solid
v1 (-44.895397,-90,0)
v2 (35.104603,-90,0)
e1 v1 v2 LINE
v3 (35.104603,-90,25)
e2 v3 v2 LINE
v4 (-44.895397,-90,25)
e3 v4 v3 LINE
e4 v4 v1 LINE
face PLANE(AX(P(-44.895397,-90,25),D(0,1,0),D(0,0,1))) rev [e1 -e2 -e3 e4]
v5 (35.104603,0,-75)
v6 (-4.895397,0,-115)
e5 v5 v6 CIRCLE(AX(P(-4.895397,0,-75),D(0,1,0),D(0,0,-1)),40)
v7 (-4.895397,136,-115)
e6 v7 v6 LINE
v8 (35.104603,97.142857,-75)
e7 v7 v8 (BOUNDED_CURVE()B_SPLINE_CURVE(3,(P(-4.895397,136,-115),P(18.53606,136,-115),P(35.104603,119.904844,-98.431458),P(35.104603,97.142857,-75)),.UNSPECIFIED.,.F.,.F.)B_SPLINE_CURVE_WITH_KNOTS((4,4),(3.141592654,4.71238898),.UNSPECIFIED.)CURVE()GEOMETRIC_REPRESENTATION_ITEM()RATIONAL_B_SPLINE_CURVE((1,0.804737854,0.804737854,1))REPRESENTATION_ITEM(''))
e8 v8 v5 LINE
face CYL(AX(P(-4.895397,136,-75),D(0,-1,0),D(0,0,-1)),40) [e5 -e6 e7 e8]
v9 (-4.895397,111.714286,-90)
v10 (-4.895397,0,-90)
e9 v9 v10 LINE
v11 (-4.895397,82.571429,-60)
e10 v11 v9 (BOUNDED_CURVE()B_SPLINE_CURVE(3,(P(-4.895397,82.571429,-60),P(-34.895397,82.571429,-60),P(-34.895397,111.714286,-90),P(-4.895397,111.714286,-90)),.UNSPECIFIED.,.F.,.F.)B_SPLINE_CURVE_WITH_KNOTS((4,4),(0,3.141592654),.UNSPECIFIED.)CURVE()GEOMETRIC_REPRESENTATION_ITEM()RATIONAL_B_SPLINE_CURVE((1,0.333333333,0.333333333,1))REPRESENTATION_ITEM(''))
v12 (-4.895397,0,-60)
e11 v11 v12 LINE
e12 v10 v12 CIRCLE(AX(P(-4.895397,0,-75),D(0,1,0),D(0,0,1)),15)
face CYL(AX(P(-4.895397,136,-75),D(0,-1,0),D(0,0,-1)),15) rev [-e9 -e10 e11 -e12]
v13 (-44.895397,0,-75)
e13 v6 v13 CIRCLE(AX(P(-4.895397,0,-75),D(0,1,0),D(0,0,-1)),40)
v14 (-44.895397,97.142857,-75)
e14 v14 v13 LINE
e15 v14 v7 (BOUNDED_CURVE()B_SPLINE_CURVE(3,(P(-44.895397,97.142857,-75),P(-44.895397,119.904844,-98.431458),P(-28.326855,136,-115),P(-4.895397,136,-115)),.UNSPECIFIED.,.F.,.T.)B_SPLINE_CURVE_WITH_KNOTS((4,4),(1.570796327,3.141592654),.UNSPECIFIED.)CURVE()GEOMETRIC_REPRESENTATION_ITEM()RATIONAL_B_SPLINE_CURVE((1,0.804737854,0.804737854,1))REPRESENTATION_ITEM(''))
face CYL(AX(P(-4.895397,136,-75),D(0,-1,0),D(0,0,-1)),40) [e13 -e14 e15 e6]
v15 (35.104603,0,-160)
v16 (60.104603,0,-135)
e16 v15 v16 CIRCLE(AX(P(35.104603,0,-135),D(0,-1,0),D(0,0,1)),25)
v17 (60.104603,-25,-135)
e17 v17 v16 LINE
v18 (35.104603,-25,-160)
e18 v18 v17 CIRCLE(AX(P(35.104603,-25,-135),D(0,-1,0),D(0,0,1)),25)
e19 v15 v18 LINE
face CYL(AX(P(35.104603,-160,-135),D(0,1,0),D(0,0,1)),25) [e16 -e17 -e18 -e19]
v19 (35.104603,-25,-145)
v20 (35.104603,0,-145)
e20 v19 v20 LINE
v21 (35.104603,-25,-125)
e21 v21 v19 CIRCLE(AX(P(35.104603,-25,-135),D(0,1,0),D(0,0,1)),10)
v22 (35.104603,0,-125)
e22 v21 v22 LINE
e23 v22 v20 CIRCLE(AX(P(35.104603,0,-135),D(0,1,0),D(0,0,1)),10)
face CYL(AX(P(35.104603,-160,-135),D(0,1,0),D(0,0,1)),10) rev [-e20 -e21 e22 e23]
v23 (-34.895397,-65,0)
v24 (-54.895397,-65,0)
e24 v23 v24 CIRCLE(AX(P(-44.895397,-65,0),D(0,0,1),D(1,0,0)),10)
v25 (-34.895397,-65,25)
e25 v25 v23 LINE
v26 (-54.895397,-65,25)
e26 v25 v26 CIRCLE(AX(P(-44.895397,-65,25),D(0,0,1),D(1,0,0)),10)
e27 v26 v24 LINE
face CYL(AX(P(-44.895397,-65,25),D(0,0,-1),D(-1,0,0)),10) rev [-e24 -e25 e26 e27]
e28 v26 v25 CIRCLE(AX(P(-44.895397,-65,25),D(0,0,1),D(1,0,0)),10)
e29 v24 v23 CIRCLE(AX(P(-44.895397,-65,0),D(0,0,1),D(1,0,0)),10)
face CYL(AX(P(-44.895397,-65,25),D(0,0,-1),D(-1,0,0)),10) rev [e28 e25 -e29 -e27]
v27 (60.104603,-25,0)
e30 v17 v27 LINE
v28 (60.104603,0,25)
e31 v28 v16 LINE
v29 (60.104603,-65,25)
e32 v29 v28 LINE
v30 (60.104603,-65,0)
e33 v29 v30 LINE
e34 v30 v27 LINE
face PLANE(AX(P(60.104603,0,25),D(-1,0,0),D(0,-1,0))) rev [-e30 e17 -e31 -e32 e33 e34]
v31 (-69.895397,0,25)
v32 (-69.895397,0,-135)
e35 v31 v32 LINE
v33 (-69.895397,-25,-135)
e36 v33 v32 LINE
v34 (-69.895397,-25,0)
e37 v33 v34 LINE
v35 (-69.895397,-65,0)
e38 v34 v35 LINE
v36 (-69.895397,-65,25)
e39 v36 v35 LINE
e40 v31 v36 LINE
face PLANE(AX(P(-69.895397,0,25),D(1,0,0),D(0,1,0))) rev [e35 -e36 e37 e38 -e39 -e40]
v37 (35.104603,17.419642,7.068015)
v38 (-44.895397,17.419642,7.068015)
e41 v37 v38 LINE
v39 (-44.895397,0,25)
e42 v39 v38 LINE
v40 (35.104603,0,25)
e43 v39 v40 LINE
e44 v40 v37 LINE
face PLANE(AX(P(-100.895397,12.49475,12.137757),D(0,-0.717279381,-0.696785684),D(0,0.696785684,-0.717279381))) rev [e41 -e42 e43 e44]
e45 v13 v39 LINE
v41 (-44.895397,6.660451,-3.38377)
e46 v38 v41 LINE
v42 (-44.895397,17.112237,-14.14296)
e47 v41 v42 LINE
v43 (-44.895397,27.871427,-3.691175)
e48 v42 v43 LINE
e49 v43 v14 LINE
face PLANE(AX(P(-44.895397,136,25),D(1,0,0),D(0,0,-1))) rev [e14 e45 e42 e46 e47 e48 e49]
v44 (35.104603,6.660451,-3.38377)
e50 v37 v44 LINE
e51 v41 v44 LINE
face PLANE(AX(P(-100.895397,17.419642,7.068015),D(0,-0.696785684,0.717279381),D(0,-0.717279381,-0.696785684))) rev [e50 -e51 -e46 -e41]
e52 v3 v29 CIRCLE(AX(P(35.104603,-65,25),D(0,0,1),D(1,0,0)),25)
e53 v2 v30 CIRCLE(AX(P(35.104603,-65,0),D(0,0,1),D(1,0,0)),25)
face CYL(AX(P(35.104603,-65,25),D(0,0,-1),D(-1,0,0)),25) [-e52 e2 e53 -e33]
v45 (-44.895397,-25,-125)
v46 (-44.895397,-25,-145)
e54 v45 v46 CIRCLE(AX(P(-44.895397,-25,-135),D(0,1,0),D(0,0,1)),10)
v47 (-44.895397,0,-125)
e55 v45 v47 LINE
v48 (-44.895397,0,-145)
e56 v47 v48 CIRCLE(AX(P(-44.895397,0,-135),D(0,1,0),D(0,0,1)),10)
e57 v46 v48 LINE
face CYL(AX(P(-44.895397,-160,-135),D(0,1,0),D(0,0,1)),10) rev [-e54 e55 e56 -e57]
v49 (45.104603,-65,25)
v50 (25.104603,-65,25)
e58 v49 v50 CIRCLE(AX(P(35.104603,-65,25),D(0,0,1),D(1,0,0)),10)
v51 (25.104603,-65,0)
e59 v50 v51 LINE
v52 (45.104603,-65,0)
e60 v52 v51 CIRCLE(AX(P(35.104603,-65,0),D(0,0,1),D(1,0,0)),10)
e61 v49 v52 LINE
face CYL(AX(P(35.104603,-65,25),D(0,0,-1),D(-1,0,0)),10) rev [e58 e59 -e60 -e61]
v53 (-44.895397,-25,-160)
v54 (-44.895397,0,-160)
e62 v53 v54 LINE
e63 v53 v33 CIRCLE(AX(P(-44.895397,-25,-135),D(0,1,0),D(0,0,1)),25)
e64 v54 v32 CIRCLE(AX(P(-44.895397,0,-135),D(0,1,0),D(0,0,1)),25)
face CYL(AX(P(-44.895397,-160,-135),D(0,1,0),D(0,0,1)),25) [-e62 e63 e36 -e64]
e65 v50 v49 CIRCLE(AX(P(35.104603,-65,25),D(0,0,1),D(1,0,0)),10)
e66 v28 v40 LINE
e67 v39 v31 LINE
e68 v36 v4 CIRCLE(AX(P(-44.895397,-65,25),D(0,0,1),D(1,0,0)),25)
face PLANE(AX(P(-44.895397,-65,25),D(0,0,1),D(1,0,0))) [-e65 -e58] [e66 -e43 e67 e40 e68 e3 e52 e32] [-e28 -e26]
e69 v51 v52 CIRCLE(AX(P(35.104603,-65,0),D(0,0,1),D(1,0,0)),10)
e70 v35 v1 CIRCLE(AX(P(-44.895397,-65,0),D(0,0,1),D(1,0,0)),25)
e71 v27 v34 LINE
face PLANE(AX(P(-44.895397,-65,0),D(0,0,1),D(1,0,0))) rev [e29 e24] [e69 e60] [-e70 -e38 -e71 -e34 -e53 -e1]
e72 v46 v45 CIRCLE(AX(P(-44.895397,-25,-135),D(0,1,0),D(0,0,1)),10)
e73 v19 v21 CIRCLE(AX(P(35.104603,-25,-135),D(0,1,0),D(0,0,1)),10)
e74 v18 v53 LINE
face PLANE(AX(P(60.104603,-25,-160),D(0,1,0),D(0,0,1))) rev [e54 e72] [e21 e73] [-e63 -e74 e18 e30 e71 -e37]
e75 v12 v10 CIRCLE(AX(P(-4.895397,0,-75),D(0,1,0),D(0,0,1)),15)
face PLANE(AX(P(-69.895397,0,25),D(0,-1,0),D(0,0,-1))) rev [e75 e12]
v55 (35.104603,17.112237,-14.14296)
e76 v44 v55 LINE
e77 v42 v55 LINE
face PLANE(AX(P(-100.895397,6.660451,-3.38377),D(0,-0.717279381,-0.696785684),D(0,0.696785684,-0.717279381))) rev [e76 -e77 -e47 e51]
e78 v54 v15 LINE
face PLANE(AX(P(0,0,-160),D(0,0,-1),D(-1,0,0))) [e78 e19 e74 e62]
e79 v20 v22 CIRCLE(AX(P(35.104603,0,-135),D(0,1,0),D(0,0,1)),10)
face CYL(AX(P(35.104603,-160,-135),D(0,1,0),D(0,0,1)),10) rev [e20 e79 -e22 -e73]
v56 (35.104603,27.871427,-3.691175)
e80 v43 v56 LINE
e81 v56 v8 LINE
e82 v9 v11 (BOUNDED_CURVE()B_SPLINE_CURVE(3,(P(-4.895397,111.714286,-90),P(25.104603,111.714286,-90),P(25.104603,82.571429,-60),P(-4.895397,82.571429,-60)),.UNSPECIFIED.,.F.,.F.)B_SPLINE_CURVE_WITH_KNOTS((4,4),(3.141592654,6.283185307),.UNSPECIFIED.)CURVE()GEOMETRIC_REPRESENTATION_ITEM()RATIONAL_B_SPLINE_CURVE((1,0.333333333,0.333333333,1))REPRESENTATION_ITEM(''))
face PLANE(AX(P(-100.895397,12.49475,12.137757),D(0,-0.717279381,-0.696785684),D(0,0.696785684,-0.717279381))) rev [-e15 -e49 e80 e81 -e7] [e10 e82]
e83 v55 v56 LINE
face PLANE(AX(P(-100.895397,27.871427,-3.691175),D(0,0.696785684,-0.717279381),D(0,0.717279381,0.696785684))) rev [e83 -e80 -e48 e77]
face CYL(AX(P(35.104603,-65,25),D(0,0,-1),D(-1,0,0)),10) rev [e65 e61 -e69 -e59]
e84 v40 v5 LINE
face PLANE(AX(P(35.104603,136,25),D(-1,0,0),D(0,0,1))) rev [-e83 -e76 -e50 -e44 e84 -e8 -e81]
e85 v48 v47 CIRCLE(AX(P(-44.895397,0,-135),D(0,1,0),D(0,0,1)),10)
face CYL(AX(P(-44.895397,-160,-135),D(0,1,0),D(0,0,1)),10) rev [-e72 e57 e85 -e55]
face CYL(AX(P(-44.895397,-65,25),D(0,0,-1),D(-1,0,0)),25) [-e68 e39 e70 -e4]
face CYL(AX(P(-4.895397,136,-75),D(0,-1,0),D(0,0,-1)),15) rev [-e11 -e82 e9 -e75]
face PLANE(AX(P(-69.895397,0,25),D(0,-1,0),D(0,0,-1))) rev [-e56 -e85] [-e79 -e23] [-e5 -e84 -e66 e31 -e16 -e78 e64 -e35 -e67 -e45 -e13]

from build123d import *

# Parameters (mm, degrees)
BASE_PLATE_SKETCH_R      = 10
BASE_PLATE_DEPTH         = 25
FLANGE_SKETCH_W          = 130
FLANGE_SKETCH_H          = 25
FLANGE_DEPTH             = 160
FLANGE_PROFILE_CUT_DEPTH = 160
HOLES_SKETCH_R           = 10
HOLES_CUT_DEPTH          = 160
LUG_SKETCH_R             = 15
LUG_DEPTH                = 136
LUG_45DEG_TRIM_DEPTH     = 136
LUG_NOTCH_DEPTH          = 136


with BuildPart() as part:
    # Base Plate Sketch → Base Plate (new body)
    with BuildSketch(Plane.XY):
        with BuildLine():
            Line((-69.89539749, 0), (60.10460251, 0))
            Line((60.10460251, 0), (60.10460251, -65))
            ThreePointArc((60.10460251, -65), (52.78227204, -82.67766953), (35.10460251, -90))
            Line((35.10460251, -90), (-44.89539749, -90))
            ThreePointArc((-44.89539749, -90), (-62.573067019, -82.67766953), (-69.89539749, -65))
            Line((-69.89539749, -65), (-69.89539749, 0))
        make_face()
        with Locations((-44.89539749, -65)):
            Circle(BASE_PLATE_SKETCH_R, mode=Mode.SUBTRACT)
        with Locations((35.10460251, -65)):
            Circle(BASE_PLATE_SKETCH_R, mode=Mode.SUBTRACT)
    extrude(amount=BASE_PLATE_DEPTH)

    # Flange Sketch → Flange (add)
    with BuildSketch(Plane(origin=(0, 0, 0), x_dir=(-1, 0, 0), z_dir=(0, 0, -1))):
        with Locations((4.89539749, -12.5)):
            Rectangle(FLANGE_SKETCH_W, FLANGE_SKETCH_H)
    extrude(amount=FLANGE_DEPTH)

    # Flange Profile Cut Sketch → Flange Profile Cut (cut)
    with BuildSketch(Plane(origin=(0, 0, 0), x_dir=(1, 0, 0), z_dir=(0, 1, 0))):
        with BuildLine():
            Line((60.10460251, 160), (35.10460251, 160))
            ThreePointArc((35.10460251, 160), (52.78227204, 152.67766953), (60.10460251, 135))
            Line((60.10460251, 135), (60.10460251, 160))
        make_face()
        with BuildLine():
            ThreePointArc((-69.89539749, 135), (-62.573067019, 152.67766953), (-44.89539749, 160))
            Line((-44.89539749, 160), (-69.89539749, 160))
            Line((-69.89539749, 160), (-69.89539749, 135))
        make_face()
    extrude(amount=-FLANGE_PROFILE_CUT_DEPTH, mode=Mode.SUBTRACT)

    # Holes Sketch → Holes Cut (cut)
    with BuildSketch(Plane(origin=(0, 0, 0), x_dir=(1, 0, 0), z_dir=(0, 1, 0))):
        with Locations(Location((-44.89539749, 135, 0), (0, 0, 270))):
            Circle(HOLES_SKETCH_R)
        with Locations(Location((35.10460251, 135, 0), (0, 0, 270))):
            Circle(HOLES_SKETCH_R)
    extrude(amount=-HOLES_CUT_DEPTH, mode=Mode.SUBTRACT)

    # Lug Sketch → Lug (add)
    with BuildSketch(Plane(origin=(0, 0, 0), x_dir=(1, 0, 0), z_dir=(0, 1, 0))):
        with BuildLine():
            Line((-44.89539749, -25), (35.10460251, -25))
            Line((35.10460251, -25), (35.10460251, 75))
            ThreePointArc((35.10460251, 75), (-4.89539749, 115), (-44.89539749, 75))
            Line((-44.89539749, 75), (-44.89539749, -25))
        make_face()
        with Locations(Location((-4.89539749, 75, 0), (0, 0, 270))):
            Circle(LUG_SKETCH_R, mode=Mode.SUBTRACT)
    extrude(amount=LUG_DEPTH)

    # Lug 45deg Trim Sketch → Lug 45deg Trim (cut)
    with BuildSketch(Plane(origin=(35.10460251, 0, 0), x_dir=(0, 0, -1), z_dir=(1, 0, 0))):
        Polygon((-25, 0), (-25, 136), (115, 136), align=None)
    extrude(amount=-LUG_45DEG_TRIM_DEPTH, mode=Mode.SUBTRACT)

    # Lug Notch Sketch → Lug Notch (cut)
    with BuildSketch(Plane(origin=(35.10460251, 0, 0), x_dir=(0, 0, -1), z_dir=(1, 0, 0))):
        Polygon((-7.068015479, 17.419642107), (3.691175234, 27.871427371), (14.142960498, 17.112236658), (3.383769785, 6.660451394), align=None)
    extrude(amount=-LUG_NOTCH_DEPTH, mode=Mode.SUBTRACT)


solid = part.part
